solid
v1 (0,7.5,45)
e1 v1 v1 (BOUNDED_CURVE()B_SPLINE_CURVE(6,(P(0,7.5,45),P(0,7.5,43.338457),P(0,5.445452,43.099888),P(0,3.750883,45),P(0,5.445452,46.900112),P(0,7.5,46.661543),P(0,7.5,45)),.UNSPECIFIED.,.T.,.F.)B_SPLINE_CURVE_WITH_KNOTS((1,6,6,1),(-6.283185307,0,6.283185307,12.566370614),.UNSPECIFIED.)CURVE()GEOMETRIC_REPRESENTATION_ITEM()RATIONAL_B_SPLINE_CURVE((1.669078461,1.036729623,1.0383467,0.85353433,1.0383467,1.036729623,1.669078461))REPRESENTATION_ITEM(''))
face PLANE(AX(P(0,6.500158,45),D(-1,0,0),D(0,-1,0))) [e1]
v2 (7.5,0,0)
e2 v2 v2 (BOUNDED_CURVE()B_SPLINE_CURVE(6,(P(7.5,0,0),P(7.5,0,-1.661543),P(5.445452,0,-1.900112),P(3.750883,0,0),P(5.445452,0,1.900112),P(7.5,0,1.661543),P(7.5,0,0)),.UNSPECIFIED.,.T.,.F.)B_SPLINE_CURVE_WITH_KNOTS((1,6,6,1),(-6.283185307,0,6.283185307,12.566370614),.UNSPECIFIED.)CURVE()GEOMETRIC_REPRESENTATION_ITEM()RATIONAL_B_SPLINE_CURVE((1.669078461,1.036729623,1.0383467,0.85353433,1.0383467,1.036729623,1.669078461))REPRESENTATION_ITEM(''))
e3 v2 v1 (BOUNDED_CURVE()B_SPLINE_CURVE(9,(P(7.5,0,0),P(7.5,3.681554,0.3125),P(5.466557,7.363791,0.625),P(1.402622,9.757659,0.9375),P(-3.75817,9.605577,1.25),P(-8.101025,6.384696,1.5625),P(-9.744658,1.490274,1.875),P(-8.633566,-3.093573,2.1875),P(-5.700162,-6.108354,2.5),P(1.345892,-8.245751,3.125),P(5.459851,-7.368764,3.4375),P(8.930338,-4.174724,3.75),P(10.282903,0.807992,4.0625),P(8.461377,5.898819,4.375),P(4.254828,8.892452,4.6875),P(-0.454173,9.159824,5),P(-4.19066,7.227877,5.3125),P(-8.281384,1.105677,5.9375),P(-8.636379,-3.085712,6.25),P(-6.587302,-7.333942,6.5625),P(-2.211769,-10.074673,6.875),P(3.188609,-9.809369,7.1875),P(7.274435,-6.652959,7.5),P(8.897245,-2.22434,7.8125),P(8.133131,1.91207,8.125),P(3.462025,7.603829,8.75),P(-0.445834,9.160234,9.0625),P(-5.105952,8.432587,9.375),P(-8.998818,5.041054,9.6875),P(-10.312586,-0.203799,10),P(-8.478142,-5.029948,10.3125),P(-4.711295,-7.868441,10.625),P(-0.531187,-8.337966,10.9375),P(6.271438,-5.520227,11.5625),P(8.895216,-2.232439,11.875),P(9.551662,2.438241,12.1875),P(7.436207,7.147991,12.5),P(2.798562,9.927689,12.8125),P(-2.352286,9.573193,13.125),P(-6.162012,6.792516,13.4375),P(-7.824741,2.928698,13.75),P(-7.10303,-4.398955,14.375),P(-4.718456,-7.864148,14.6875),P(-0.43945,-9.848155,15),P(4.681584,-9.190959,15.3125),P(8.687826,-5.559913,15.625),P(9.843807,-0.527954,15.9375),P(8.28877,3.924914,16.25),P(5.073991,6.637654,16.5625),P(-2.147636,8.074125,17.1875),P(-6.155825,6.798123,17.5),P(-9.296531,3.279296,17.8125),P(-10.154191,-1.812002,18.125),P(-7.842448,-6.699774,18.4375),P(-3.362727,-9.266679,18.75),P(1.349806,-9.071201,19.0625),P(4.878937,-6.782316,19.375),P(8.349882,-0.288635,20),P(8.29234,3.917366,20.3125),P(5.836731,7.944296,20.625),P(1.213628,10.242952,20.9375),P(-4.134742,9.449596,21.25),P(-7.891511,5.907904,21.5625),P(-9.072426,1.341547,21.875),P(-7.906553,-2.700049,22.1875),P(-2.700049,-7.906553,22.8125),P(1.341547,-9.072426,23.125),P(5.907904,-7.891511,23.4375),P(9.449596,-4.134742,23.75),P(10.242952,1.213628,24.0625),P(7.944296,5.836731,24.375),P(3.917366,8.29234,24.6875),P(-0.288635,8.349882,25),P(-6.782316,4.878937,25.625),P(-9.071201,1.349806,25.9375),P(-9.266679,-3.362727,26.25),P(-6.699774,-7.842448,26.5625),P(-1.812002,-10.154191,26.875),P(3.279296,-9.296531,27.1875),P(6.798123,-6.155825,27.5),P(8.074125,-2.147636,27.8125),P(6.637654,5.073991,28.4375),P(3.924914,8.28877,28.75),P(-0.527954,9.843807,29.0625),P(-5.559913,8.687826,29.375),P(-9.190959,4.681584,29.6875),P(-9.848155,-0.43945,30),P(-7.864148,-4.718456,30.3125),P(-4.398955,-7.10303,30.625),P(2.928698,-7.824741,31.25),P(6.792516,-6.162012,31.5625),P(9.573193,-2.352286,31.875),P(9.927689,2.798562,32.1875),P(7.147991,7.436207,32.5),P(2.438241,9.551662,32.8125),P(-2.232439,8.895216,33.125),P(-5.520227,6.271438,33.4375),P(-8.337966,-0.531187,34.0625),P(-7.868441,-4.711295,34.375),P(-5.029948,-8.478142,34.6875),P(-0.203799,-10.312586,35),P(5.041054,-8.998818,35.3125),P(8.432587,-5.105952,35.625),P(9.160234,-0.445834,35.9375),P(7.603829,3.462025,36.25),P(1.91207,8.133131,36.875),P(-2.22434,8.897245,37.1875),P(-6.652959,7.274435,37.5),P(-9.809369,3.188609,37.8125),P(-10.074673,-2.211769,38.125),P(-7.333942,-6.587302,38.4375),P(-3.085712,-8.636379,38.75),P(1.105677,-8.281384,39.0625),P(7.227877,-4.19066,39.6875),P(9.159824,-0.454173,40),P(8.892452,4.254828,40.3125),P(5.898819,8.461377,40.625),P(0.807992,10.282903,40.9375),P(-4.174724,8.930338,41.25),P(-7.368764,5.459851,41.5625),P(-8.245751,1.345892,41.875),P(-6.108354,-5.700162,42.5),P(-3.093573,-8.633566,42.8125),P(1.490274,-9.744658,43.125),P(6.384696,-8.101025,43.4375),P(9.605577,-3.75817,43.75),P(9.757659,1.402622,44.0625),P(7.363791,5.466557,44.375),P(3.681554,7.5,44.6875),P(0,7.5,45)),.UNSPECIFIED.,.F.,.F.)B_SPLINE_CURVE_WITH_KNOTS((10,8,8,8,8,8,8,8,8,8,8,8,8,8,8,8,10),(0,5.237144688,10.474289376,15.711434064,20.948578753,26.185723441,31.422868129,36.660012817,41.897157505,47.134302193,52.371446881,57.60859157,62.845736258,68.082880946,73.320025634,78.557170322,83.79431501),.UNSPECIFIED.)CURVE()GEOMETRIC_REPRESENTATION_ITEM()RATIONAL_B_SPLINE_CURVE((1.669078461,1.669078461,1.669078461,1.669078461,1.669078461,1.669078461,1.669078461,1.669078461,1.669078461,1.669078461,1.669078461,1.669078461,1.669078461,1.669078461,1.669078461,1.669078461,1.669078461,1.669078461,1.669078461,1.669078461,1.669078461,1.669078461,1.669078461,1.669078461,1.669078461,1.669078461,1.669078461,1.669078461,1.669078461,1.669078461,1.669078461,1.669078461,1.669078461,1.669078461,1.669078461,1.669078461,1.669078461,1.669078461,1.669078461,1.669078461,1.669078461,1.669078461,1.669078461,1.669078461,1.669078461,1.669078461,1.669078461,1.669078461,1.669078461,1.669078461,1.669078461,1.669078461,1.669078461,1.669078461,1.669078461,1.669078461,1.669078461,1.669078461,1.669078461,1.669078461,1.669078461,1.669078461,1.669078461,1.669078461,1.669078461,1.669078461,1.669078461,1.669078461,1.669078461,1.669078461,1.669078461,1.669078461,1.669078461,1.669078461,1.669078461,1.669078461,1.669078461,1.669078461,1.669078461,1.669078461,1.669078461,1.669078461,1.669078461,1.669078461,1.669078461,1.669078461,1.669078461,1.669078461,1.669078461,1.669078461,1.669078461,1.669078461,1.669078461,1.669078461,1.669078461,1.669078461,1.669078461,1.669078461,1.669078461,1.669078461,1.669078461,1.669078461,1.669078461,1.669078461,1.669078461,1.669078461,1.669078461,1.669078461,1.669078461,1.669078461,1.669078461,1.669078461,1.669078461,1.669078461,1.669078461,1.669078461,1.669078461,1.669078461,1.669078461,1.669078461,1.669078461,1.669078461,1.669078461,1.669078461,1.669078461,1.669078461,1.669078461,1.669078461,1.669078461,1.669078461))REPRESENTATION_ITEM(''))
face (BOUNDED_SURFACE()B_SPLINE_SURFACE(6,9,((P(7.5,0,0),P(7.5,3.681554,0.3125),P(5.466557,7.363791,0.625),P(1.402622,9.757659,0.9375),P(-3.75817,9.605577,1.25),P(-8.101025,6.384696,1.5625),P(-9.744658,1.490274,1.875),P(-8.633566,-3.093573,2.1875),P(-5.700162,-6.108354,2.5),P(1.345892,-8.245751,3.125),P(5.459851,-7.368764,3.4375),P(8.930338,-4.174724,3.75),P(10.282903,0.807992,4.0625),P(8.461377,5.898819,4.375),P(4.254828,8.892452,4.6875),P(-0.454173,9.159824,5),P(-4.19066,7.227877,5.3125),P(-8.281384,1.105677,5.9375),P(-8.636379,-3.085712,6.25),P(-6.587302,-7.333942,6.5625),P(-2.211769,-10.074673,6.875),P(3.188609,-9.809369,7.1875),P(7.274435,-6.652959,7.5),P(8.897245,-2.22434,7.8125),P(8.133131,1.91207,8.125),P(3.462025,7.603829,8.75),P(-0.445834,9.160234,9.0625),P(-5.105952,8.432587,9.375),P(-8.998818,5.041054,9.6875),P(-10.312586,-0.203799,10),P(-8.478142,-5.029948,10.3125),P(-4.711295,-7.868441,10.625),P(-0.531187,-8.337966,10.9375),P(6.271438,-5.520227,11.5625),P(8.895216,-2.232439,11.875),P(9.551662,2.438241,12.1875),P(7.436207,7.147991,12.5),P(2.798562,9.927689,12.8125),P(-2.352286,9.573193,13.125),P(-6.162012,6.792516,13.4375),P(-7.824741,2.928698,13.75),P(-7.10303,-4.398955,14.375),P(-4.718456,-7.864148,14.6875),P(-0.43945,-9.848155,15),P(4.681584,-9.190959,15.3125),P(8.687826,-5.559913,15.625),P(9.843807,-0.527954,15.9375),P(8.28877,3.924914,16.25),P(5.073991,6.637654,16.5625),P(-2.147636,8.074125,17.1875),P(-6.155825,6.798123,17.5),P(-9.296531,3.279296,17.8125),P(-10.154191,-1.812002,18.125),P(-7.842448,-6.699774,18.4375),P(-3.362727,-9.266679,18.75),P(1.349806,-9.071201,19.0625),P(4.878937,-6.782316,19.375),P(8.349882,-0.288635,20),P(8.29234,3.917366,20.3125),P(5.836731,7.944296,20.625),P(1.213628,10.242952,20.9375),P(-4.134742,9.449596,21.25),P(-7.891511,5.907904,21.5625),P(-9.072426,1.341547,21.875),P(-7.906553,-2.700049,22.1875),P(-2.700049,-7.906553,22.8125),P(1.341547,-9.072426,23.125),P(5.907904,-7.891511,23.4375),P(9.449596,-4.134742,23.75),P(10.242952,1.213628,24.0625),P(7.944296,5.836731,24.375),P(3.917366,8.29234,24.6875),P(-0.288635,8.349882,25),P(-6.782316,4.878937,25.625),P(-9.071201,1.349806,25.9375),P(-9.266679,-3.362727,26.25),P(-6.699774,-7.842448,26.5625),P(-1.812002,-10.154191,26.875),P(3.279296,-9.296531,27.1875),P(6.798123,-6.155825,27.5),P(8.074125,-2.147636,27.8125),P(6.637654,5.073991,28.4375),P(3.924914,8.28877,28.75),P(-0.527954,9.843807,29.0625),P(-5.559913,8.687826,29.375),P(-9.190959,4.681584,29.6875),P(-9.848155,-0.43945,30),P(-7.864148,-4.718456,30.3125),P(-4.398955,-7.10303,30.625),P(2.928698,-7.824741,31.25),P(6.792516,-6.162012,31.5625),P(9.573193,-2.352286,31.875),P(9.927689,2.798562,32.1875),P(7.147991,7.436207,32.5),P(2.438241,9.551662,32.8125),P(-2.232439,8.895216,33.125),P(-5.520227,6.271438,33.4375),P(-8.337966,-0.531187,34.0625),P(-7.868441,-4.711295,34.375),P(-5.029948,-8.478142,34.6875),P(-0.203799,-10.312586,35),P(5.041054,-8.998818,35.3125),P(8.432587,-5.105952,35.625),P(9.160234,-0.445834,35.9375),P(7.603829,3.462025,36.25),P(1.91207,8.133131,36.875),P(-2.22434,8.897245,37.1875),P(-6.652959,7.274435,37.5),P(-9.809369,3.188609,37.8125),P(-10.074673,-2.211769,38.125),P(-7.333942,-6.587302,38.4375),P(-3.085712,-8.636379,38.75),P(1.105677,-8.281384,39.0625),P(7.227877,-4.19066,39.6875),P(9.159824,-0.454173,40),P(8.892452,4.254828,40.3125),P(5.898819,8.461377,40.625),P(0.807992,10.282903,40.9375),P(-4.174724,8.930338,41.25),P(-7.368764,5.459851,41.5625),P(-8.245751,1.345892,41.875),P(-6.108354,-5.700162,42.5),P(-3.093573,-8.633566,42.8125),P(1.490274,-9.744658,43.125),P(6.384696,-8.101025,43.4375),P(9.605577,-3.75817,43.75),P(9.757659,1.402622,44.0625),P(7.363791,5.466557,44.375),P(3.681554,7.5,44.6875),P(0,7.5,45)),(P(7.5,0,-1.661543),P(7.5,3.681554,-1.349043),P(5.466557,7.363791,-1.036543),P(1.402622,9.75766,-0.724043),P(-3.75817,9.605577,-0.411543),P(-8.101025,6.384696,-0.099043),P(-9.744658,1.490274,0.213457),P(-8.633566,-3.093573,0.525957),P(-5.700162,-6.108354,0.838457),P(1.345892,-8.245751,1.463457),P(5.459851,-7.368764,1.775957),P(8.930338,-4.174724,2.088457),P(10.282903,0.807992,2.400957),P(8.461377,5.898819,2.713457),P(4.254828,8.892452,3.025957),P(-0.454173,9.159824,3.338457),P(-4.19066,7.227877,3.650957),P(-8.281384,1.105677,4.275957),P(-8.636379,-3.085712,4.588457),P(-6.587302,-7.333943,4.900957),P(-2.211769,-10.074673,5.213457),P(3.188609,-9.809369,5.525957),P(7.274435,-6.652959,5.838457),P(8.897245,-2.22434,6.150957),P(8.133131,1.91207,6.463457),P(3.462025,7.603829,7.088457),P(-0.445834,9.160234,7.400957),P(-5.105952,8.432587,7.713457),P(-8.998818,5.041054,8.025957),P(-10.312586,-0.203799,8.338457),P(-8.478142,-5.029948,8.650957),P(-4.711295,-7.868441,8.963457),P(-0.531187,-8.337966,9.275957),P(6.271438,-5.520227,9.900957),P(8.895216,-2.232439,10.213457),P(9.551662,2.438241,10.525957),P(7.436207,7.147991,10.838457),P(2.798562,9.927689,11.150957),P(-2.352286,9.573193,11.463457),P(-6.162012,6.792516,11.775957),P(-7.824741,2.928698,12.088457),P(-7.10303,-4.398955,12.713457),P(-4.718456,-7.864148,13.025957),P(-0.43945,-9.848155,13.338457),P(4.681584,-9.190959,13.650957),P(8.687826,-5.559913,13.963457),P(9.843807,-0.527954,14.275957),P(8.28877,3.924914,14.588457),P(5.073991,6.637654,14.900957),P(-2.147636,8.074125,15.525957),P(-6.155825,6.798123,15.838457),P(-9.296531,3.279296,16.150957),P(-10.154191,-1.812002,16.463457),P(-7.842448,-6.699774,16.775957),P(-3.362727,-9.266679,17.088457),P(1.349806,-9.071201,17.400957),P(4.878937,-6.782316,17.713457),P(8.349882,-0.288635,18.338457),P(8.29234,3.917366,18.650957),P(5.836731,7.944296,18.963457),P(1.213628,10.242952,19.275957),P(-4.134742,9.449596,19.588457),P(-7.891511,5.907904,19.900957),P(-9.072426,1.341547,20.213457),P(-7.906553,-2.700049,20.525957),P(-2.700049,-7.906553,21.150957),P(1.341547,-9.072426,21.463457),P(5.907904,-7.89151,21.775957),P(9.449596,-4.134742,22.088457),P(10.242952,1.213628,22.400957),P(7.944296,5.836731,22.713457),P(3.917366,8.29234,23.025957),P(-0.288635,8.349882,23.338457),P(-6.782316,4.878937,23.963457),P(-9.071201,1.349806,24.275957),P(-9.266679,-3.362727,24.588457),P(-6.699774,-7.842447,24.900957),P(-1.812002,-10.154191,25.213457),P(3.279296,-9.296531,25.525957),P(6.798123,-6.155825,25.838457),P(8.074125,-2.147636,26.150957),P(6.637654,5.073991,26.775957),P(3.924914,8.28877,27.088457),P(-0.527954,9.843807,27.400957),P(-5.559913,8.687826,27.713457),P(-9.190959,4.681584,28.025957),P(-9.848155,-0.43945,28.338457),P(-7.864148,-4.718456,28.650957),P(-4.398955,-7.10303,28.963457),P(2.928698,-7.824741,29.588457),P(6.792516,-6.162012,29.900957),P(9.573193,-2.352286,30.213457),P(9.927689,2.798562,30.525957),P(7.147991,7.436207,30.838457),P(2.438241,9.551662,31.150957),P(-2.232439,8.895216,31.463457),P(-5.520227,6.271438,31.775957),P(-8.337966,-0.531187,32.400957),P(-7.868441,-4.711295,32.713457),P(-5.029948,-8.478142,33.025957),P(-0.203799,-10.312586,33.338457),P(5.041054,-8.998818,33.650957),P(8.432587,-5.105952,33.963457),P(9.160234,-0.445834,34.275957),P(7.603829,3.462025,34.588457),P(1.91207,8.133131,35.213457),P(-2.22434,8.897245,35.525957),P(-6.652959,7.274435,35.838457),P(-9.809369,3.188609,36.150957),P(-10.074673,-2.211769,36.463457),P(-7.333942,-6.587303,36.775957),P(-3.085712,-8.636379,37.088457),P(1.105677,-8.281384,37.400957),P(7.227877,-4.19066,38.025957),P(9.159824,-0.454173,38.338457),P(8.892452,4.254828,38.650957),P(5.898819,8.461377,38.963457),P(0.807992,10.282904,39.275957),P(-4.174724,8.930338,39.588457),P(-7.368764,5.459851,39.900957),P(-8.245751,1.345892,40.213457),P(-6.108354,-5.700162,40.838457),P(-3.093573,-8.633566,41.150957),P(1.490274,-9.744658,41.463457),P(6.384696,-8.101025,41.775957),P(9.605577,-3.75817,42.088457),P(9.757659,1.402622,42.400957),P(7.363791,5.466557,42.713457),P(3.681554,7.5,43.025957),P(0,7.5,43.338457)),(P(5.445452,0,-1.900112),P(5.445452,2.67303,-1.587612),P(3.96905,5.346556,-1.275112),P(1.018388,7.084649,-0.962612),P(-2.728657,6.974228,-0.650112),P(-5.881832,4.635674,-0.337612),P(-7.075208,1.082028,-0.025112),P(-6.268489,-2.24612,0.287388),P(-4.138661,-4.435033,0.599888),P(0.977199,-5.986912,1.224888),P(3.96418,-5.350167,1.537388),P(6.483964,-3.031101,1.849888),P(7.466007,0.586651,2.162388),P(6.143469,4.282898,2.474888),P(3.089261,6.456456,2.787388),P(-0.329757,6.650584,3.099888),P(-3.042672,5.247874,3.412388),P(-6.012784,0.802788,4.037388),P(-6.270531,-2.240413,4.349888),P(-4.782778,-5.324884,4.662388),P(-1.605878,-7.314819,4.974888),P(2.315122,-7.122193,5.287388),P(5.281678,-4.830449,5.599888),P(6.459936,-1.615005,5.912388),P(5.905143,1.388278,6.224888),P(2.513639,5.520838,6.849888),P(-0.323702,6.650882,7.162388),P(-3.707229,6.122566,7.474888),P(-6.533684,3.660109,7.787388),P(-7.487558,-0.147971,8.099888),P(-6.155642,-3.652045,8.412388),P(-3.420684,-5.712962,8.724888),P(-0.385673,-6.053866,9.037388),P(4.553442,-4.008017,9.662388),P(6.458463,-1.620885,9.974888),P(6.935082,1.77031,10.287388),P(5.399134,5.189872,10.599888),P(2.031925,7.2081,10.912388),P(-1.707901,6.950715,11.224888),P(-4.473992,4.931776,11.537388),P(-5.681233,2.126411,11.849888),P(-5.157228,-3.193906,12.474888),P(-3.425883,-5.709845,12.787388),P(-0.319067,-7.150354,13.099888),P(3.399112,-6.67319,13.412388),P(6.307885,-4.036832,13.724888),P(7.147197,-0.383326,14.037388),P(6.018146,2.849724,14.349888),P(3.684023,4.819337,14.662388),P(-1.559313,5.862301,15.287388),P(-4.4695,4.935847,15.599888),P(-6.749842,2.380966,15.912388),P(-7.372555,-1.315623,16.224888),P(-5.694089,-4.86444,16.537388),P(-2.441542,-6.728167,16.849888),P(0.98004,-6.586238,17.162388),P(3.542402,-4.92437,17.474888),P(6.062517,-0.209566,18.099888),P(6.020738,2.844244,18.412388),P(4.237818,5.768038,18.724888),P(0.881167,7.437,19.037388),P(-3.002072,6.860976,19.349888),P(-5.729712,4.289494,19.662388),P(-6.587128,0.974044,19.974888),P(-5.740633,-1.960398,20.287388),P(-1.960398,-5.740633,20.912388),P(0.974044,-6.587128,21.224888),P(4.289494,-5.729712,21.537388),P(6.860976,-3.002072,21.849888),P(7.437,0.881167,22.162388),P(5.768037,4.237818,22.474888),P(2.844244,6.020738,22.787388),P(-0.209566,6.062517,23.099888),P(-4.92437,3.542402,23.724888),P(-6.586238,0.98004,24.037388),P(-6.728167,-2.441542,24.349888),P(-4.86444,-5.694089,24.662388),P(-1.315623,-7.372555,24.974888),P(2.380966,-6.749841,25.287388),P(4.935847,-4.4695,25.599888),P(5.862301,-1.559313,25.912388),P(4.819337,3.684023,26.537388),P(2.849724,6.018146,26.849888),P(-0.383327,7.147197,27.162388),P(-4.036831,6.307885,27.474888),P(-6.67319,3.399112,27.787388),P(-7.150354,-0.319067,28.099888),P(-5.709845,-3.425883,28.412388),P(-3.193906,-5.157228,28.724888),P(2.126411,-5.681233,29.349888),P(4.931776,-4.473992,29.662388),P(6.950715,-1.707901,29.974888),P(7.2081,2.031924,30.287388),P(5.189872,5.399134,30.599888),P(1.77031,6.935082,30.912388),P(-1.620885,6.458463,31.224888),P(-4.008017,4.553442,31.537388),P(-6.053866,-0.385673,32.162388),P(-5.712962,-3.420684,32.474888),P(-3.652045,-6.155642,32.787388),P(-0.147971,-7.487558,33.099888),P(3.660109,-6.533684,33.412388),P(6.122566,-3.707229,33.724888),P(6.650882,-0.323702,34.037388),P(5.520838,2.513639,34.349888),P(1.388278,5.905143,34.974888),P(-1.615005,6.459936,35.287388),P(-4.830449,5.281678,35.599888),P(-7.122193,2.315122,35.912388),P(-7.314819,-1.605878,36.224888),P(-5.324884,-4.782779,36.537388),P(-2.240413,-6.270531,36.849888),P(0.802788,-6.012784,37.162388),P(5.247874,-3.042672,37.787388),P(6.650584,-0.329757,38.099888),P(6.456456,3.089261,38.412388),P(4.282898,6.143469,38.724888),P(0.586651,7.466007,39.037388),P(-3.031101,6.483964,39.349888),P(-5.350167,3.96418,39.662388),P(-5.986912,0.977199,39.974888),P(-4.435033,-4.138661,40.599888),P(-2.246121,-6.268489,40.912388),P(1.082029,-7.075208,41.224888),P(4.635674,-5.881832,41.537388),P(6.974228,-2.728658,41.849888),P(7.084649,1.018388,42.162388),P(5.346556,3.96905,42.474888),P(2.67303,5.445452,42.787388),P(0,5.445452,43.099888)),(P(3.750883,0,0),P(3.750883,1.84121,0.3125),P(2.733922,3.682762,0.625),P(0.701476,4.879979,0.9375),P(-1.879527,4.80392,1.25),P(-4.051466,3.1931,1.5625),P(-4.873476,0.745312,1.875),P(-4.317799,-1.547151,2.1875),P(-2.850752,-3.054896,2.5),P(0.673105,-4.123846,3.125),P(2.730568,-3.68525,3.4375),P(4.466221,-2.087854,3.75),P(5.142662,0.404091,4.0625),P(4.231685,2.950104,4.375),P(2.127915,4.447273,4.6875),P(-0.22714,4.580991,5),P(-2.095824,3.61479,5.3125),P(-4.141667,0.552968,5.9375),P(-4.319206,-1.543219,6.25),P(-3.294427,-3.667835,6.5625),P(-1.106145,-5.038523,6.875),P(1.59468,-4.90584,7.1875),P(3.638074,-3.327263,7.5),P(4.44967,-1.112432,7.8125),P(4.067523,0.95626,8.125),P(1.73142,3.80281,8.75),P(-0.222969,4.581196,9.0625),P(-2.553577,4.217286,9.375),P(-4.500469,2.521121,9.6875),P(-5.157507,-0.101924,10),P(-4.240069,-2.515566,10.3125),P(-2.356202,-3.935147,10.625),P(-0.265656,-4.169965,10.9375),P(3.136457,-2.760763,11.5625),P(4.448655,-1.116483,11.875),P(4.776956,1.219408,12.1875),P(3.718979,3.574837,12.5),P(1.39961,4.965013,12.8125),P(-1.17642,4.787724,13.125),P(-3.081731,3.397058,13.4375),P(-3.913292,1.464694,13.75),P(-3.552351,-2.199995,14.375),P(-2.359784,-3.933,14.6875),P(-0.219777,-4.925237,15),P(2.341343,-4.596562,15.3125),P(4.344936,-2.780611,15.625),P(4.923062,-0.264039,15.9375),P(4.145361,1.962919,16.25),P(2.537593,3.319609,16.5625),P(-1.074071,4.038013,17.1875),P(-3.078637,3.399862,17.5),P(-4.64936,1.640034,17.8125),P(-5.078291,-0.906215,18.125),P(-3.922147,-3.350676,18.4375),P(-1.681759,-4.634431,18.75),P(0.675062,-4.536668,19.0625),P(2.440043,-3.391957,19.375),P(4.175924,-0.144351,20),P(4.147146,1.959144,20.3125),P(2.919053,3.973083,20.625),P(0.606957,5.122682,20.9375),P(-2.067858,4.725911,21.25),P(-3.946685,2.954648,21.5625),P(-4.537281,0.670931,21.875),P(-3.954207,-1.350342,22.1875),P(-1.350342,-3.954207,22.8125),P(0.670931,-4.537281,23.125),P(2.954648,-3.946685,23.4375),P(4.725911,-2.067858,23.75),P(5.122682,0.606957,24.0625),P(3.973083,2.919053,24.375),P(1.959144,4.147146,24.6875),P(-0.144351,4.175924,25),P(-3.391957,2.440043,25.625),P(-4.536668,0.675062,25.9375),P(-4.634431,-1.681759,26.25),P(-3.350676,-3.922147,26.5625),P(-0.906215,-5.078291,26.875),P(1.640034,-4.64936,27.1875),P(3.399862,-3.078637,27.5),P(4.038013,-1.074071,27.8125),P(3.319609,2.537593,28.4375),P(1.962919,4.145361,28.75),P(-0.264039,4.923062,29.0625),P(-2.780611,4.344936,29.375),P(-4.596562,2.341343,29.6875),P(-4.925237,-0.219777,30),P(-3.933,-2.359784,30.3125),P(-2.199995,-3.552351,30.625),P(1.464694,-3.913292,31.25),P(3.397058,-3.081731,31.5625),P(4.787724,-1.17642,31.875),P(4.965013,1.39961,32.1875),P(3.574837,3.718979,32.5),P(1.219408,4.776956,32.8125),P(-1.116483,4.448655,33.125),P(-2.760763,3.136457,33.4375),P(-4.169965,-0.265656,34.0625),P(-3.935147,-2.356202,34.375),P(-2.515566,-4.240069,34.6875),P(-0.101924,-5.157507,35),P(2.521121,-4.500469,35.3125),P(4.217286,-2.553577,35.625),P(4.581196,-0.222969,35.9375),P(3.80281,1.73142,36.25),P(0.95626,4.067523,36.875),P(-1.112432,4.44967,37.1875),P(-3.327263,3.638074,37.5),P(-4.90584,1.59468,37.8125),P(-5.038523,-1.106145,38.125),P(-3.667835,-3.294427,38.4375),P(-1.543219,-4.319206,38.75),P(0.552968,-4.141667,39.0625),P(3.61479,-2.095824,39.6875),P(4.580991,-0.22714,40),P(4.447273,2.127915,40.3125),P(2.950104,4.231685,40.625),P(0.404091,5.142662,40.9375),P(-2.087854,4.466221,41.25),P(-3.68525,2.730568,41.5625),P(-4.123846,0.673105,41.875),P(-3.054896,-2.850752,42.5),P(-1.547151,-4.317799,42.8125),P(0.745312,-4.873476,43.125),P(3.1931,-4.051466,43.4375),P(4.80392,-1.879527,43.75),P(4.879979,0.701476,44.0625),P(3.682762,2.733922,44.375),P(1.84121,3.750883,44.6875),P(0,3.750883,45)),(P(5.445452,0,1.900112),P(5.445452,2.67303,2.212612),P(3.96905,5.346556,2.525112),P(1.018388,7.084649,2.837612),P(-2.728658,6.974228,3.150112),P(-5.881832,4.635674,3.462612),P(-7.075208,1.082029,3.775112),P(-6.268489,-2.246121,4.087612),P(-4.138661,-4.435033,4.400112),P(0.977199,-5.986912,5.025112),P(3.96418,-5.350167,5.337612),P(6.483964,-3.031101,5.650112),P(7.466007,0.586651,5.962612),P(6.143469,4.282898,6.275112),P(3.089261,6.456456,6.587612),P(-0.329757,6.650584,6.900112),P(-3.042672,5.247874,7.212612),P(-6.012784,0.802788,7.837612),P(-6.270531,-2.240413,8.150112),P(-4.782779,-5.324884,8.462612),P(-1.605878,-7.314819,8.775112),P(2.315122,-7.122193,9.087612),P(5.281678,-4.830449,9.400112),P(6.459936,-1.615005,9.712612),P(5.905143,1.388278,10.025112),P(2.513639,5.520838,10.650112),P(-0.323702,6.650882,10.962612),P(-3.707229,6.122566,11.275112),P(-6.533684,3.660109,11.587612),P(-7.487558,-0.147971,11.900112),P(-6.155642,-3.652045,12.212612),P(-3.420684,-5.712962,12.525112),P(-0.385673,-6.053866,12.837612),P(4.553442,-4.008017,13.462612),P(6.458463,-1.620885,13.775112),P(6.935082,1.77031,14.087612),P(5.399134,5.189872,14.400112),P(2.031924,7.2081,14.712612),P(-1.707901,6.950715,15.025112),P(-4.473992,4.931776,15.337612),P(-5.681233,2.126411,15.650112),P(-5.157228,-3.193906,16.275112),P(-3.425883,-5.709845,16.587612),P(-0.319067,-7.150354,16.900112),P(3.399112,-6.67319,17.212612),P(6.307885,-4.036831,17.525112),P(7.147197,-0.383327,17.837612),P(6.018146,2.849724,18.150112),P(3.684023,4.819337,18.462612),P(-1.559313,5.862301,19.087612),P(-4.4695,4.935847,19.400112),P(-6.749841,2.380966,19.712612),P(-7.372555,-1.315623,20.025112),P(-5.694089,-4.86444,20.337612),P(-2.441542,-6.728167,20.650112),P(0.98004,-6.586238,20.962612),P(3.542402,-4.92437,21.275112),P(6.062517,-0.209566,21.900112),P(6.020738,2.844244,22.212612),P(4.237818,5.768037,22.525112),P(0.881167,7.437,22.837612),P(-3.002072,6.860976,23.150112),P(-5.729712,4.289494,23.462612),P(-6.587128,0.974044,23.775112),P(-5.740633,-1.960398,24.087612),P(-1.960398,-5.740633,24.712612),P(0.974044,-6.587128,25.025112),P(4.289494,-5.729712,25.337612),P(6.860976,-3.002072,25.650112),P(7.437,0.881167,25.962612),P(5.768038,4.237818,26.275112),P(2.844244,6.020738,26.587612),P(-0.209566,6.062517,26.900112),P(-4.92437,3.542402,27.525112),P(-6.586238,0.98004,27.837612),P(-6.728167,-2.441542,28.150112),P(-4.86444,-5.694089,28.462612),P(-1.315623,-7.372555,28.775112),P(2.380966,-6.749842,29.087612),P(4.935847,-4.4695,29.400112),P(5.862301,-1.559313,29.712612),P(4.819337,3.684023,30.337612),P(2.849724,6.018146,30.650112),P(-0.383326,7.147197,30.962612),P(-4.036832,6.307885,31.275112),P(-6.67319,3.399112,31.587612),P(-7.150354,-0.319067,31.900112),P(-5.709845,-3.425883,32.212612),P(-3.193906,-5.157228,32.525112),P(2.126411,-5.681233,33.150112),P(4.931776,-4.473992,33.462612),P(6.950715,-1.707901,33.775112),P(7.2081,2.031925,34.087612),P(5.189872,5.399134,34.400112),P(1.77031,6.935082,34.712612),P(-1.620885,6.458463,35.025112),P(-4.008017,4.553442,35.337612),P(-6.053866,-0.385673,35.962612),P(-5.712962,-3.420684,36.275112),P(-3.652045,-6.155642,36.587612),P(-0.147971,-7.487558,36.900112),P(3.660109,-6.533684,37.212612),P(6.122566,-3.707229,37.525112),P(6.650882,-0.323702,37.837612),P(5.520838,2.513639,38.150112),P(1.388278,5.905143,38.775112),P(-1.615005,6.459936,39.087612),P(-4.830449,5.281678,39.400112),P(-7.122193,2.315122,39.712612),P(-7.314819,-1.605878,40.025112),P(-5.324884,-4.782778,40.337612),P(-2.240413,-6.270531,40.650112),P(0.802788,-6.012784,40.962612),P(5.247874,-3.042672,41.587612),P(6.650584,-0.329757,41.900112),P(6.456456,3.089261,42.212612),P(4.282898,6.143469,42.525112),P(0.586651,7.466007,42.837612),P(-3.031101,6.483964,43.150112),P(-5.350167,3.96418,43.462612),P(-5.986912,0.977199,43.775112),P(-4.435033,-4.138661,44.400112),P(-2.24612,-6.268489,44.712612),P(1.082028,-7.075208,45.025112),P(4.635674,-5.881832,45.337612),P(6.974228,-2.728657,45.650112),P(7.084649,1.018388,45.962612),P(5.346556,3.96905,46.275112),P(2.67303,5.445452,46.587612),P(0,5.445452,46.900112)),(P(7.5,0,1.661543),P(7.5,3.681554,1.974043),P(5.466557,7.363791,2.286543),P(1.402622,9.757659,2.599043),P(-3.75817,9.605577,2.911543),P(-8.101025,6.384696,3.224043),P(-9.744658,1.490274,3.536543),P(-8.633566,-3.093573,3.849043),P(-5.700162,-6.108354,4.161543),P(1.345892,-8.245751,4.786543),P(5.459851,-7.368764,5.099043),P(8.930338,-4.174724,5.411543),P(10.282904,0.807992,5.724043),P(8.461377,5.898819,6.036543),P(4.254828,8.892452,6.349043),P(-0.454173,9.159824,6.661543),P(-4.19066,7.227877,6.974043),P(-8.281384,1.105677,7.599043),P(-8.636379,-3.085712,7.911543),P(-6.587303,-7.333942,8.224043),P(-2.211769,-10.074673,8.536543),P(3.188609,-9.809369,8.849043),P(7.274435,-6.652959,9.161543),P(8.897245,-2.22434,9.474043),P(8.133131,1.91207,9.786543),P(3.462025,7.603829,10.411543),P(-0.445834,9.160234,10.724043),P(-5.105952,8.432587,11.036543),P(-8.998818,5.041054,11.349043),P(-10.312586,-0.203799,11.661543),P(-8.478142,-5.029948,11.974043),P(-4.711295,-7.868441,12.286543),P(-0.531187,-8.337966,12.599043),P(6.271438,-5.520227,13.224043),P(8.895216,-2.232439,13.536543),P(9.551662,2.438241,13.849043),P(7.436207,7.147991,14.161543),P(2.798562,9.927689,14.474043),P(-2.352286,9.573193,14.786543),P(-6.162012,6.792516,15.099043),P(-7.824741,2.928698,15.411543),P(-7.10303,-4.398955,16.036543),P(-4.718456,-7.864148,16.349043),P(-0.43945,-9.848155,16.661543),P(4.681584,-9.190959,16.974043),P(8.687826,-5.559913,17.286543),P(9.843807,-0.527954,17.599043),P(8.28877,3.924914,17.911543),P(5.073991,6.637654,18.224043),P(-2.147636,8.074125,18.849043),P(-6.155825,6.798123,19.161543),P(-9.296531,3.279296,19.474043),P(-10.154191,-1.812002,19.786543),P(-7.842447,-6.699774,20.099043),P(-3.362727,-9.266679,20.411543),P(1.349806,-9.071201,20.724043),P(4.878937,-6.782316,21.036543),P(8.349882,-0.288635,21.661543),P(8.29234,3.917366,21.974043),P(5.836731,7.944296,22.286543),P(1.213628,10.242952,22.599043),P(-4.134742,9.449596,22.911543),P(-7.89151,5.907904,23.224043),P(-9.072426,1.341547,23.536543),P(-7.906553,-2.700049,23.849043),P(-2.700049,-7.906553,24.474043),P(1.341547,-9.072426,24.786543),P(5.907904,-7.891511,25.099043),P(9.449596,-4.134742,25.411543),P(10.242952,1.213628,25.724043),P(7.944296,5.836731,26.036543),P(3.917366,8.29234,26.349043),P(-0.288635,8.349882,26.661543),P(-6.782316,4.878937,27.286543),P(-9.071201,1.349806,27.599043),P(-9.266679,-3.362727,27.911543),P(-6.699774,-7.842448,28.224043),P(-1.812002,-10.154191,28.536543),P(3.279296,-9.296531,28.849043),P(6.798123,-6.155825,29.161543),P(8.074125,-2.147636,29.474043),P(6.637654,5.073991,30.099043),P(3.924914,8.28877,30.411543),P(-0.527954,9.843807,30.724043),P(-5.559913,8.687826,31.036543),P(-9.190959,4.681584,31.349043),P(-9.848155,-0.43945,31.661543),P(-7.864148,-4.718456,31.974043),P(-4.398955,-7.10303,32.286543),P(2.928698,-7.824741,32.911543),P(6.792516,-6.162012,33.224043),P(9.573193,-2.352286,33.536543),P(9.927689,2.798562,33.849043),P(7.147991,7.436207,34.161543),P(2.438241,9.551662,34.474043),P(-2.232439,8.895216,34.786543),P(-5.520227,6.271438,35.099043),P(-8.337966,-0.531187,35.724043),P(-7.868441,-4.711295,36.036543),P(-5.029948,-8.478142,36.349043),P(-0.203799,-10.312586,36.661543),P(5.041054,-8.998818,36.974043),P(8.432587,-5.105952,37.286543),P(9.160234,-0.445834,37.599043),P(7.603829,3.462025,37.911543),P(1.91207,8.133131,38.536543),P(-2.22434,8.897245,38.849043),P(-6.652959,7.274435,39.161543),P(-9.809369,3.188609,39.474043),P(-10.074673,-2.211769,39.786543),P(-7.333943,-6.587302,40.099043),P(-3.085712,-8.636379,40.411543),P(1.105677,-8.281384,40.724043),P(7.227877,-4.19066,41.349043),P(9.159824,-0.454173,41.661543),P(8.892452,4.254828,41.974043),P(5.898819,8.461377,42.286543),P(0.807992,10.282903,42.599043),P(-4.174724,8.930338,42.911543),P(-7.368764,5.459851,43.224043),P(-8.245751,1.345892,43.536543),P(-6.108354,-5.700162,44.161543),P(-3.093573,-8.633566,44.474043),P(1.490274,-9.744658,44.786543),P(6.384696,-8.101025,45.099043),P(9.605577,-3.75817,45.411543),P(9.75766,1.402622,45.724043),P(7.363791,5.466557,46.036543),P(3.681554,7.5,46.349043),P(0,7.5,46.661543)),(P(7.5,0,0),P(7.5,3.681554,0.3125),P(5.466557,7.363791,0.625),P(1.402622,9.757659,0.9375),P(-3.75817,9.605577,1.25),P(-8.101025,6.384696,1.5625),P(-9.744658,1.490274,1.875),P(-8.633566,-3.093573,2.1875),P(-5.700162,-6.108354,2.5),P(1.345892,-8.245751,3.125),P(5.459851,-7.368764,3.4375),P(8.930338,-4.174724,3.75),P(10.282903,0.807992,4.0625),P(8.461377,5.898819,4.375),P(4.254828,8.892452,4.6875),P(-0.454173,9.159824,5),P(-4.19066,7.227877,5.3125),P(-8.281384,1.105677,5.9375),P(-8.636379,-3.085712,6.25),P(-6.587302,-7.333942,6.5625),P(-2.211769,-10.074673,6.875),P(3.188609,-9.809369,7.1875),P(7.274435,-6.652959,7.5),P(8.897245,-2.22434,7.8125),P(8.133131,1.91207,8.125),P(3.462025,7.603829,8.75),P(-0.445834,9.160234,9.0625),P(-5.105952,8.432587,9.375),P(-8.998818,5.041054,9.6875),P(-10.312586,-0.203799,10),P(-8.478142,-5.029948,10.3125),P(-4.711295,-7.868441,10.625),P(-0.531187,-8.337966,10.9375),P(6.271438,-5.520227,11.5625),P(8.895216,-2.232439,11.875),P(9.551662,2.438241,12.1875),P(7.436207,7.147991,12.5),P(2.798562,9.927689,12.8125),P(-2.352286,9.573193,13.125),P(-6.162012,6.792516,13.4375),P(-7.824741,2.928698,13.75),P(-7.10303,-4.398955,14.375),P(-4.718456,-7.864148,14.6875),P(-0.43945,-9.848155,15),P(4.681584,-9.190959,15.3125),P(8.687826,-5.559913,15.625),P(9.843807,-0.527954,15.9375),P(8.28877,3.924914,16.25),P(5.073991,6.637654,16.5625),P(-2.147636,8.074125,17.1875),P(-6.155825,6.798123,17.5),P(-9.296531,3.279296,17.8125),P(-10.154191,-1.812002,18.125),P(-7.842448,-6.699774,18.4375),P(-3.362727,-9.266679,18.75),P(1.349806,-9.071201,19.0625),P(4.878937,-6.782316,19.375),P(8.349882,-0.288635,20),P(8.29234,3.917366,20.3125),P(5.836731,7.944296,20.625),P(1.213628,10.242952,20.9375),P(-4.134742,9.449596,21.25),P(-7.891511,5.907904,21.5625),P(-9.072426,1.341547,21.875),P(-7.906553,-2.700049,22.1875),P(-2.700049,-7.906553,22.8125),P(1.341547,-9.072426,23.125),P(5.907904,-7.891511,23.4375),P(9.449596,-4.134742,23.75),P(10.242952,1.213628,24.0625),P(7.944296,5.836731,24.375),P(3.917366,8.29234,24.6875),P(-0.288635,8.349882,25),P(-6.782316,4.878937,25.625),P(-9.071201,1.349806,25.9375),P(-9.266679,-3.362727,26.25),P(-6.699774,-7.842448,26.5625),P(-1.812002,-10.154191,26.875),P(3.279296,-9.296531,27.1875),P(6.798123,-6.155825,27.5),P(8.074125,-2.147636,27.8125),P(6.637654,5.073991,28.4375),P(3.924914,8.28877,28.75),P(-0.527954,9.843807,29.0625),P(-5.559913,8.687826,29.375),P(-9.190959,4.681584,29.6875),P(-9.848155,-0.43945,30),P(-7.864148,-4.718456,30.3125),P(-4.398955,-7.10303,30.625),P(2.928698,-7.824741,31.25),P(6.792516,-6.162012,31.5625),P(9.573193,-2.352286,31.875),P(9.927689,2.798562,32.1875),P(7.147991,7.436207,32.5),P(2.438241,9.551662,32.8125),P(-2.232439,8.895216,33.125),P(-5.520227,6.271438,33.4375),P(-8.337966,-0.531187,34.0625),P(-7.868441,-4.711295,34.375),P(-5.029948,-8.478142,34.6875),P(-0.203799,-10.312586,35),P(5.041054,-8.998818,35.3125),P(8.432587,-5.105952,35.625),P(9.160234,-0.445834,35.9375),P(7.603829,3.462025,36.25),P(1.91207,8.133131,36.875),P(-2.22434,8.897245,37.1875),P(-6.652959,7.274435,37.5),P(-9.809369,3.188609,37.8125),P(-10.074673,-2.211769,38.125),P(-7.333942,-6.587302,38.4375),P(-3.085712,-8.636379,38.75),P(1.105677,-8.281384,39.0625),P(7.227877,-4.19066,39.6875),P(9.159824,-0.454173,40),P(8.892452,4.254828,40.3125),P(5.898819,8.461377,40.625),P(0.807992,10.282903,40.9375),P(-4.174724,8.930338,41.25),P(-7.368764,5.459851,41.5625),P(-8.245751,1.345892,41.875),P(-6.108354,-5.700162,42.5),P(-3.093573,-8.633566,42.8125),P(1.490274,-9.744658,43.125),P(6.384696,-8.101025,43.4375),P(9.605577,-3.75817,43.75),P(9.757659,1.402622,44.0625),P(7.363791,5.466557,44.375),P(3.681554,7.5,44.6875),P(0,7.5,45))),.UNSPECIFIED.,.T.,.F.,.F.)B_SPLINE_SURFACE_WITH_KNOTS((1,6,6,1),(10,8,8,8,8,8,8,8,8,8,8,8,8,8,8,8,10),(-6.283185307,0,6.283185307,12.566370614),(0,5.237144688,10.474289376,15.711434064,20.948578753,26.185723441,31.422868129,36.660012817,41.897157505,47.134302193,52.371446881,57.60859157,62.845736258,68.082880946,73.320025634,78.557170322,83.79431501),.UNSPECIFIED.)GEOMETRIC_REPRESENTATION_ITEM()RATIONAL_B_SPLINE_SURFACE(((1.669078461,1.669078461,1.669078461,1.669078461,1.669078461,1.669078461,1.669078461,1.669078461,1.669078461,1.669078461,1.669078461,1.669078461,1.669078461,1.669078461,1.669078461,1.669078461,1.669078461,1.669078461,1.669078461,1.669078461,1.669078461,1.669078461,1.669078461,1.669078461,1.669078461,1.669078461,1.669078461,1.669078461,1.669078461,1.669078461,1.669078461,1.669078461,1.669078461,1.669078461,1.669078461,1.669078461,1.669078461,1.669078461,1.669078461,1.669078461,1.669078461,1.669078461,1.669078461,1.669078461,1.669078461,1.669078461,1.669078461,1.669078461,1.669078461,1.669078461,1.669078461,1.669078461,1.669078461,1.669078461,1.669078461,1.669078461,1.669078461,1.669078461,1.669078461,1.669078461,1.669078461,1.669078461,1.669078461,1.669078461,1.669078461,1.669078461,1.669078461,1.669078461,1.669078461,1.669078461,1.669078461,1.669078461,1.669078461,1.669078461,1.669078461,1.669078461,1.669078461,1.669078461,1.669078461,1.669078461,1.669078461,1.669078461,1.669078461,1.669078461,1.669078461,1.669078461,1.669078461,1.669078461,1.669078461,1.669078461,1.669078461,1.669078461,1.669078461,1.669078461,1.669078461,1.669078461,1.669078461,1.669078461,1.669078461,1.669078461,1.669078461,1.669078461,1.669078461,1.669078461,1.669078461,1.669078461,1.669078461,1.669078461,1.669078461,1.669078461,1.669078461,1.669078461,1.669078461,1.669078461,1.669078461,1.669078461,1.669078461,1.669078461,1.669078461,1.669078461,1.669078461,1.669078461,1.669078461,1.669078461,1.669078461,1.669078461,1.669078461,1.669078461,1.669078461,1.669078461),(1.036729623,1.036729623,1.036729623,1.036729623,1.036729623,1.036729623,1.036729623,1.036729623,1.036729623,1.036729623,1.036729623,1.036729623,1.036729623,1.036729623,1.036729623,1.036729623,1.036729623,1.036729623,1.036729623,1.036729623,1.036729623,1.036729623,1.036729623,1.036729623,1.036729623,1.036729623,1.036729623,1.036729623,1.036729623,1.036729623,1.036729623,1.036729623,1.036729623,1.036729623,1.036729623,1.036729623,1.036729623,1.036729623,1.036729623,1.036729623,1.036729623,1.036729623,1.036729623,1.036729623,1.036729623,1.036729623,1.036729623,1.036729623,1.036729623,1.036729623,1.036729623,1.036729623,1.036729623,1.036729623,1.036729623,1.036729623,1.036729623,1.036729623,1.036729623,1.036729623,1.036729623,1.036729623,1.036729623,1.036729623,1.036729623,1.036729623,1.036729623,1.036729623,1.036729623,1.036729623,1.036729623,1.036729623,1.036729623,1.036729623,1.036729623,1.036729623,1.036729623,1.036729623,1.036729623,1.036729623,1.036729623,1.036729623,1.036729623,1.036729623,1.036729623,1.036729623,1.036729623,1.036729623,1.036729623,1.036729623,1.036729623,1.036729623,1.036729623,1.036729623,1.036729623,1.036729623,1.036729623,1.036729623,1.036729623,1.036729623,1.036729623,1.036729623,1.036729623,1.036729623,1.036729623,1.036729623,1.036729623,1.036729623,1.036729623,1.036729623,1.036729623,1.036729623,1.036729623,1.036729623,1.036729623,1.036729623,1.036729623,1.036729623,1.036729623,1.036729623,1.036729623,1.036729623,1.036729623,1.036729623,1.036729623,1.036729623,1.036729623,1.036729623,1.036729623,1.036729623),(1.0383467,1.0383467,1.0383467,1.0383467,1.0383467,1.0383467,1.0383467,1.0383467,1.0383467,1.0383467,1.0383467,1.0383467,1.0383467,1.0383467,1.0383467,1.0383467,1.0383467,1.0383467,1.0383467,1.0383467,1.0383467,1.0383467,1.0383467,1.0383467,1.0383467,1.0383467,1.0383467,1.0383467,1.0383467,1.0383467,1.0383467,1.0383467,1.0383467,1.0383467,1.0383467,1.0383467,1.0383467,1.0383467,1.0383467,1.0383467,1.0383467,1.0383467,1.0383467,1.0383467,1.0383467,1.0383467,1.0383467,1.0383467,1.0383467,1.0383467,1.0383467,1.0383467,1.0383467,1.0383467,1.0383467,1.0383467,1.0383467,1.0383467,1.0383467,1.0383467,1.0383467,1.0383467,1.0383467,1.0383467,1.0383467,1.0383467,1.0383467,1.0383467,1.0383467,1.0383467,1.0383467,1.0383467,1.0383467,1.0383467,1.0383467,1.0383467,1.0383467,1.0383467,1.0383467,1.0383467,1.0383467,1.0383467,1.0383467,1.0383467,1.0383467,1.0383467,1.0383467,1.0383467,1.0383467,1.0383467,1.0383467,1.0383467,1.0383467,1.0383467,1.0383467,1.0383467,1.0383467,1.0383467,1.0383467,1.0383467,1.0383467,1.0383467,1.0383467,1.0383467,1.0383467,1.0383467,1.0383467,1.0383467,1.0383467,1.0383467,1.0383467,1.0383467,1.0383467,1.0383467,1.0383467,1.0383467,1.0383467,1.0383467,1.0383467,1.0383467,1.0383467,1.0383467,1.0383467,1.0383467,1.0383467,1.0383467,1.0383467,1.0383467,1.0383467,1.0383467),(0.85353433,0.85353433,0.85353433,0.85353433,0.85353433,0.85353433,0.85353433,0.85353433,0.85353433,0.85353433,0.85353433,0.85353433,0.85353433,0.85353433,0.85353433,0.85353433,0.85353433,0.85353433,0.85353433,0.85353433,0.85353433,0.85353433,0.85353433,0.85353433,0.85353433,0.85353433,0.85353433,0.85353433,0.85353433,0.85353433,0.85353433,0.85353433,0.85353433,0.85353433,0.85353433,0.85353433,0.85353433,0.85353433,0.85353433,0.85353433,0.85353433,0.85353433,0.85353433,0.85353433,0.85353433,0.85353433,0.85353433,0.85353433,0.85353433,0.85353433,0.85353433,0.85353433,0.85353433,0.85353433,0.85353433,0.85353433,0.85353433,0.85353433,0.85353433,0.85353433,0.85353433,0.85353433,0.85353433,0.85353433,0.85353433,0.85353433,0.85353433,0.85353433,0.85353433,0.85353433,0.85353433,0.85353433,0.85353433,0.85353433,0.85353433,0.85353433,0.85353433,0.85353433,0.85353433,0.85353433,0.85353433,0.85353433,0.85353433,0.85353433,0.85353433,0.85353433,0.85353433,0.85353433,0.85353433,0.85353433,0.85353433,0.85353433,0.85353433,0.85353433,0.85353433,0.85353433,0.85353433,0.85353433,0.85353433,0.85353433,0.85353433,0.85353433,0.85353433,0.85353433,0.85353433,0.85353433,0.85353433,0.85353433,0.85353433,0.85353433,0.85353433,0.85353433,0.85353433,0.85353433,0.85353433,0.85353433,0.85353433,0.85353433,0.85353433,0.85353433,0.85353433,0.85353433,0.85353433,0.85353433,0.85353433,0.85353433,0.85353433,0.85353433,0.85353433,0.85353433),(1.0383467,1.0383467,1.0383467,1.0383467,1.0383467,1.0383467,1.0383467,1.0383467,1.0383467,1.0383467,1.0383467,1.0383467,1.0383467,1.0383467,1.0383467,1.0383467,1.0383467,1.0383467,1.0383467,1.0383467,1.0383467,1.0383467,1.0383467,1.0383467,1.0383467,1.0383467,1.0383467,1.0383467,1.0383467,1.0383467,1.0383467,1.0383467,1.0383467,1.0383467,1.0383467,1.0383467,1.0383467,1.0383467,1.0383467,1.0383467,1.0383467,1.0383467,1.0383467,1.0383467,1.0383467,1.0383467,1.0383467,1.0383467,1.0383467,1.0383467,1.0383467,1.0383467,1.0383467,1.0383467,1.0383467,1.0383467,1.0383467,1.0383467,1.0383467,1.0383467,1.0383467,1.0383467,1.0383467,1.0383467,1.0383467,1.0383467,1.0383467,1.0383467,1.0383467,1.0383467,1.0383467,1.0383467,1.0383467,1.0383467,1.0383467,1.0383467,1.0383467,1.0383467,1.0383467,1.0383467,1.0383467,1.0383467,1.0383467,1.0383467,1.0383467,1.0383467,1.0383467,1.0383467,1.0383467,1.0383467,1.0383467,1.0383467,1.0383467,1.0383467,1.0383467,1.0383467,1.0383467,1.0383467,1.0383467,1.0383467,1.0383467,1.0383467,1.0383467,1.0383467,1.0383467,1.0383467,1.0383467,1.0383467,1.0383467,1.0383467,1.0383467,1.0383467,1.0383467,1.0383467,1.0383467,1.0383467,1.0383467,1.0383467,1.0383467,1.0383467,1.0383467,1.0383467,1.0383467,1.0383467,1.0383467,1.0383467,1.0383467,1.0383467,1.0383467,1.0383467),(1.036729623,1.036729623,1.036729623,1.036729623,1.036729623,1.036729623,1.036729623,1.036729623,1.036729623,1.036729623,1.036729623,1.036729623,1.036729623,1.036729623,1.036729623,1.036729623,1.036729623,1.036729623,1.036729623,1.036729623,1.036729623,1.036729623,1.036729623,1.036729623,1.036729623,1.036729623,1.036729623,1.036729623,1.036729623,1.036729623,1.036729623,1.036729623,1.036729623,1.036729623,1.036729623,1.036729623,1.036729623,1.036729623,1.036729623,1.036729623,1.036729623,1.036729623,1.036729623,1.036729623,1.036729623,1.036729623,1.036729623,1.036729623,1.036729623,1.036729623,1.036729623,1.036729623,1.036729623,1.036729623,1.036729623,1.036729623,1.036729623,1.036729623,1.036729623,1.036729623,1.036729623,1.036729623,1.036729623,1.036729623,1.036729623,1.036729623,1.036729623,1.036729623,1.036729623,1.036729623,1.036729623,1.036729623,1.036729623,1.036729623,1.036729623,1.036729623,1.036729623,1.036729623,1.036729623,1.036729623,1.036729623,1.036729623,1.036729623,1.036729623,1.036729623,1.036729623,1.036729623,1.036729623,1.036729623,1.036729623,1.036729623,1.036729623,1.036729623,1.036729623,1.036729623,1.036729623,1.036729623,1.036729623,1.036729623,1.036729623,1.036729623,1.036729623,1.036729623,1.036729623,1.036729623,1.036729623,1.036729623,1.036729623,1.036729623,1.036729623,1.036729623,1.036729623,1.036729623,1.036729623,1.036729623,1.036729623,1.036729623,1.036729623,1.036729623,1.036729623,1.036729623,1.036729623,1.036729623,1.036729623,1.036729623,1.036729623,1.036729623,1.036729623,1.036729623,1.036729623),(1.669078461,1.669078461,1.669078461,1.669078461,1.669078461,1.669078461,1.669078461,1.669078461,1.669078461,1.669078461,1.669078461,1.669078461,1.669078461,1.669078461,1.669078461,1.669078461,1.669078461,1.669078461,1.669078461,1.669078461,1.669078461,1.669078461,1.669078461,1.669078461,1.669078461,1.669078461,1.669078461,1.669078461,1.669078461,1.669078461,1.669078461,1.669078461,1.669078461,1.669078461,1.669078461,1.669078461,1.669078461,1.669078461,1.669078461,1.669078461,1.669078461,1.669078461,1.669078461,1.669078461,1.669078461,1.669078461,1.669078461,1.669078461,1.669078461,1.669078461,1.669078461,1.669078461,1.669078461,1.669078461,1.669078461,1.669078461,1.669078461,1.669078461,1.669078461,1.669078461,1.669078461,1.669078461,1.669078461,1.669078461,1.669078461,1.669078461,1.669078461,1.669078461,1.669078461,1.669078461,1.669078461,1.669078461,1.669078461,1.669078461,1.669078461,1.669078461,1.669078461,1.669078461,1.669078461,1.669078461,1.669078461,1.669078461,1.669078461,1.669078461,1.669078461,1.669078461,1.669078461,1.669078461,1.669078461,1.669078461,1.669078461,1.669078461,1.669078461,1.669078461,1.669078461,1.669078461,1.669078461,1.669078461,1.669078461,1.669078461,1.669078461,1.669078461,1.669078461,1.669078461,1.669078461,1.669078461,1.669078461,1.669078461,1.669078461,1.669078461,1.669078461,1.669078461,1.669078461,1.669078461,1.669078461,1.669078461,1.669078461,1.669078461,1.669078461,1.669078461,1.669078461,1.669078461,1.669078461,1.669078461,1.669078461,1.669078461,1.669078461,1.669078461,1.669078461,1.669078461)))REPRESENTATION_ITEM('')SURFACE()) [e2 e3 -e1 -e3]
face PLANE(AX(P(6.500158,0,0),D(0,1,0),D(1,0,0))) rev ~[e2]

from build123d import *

# Parameters (mm, degrees)
SWEEP_1_PITCH  = 4
SWEEP_1_HEIGHT = 45
SWEEP_1_RADIUS = 6.5
SKETCH_2_R     = 1


with BuildPart() as part:
    # 扫描1: sweep along a helix
    with BuildLine() as sweep_1_path:
        Helix(SWEEP_1_PITCH, SWEEP_1_HEIGHT, SWEEP_1_RADIUS, center=(0, 0, 0), direction=(0, 0, 1))
    # 草图2 → 扫描1 (sweep)
    with BuildSketch(Plane(origin=(0, 0, 0), x_dir=(1, 0, 0), z_dir=(0, 1, 0))):
        with Locations((6.5, 0)):
            Circle(SKETCH_2_R)
    sweep(path=sweep_1_path.line, is_frenet=True)


solid = part.part
